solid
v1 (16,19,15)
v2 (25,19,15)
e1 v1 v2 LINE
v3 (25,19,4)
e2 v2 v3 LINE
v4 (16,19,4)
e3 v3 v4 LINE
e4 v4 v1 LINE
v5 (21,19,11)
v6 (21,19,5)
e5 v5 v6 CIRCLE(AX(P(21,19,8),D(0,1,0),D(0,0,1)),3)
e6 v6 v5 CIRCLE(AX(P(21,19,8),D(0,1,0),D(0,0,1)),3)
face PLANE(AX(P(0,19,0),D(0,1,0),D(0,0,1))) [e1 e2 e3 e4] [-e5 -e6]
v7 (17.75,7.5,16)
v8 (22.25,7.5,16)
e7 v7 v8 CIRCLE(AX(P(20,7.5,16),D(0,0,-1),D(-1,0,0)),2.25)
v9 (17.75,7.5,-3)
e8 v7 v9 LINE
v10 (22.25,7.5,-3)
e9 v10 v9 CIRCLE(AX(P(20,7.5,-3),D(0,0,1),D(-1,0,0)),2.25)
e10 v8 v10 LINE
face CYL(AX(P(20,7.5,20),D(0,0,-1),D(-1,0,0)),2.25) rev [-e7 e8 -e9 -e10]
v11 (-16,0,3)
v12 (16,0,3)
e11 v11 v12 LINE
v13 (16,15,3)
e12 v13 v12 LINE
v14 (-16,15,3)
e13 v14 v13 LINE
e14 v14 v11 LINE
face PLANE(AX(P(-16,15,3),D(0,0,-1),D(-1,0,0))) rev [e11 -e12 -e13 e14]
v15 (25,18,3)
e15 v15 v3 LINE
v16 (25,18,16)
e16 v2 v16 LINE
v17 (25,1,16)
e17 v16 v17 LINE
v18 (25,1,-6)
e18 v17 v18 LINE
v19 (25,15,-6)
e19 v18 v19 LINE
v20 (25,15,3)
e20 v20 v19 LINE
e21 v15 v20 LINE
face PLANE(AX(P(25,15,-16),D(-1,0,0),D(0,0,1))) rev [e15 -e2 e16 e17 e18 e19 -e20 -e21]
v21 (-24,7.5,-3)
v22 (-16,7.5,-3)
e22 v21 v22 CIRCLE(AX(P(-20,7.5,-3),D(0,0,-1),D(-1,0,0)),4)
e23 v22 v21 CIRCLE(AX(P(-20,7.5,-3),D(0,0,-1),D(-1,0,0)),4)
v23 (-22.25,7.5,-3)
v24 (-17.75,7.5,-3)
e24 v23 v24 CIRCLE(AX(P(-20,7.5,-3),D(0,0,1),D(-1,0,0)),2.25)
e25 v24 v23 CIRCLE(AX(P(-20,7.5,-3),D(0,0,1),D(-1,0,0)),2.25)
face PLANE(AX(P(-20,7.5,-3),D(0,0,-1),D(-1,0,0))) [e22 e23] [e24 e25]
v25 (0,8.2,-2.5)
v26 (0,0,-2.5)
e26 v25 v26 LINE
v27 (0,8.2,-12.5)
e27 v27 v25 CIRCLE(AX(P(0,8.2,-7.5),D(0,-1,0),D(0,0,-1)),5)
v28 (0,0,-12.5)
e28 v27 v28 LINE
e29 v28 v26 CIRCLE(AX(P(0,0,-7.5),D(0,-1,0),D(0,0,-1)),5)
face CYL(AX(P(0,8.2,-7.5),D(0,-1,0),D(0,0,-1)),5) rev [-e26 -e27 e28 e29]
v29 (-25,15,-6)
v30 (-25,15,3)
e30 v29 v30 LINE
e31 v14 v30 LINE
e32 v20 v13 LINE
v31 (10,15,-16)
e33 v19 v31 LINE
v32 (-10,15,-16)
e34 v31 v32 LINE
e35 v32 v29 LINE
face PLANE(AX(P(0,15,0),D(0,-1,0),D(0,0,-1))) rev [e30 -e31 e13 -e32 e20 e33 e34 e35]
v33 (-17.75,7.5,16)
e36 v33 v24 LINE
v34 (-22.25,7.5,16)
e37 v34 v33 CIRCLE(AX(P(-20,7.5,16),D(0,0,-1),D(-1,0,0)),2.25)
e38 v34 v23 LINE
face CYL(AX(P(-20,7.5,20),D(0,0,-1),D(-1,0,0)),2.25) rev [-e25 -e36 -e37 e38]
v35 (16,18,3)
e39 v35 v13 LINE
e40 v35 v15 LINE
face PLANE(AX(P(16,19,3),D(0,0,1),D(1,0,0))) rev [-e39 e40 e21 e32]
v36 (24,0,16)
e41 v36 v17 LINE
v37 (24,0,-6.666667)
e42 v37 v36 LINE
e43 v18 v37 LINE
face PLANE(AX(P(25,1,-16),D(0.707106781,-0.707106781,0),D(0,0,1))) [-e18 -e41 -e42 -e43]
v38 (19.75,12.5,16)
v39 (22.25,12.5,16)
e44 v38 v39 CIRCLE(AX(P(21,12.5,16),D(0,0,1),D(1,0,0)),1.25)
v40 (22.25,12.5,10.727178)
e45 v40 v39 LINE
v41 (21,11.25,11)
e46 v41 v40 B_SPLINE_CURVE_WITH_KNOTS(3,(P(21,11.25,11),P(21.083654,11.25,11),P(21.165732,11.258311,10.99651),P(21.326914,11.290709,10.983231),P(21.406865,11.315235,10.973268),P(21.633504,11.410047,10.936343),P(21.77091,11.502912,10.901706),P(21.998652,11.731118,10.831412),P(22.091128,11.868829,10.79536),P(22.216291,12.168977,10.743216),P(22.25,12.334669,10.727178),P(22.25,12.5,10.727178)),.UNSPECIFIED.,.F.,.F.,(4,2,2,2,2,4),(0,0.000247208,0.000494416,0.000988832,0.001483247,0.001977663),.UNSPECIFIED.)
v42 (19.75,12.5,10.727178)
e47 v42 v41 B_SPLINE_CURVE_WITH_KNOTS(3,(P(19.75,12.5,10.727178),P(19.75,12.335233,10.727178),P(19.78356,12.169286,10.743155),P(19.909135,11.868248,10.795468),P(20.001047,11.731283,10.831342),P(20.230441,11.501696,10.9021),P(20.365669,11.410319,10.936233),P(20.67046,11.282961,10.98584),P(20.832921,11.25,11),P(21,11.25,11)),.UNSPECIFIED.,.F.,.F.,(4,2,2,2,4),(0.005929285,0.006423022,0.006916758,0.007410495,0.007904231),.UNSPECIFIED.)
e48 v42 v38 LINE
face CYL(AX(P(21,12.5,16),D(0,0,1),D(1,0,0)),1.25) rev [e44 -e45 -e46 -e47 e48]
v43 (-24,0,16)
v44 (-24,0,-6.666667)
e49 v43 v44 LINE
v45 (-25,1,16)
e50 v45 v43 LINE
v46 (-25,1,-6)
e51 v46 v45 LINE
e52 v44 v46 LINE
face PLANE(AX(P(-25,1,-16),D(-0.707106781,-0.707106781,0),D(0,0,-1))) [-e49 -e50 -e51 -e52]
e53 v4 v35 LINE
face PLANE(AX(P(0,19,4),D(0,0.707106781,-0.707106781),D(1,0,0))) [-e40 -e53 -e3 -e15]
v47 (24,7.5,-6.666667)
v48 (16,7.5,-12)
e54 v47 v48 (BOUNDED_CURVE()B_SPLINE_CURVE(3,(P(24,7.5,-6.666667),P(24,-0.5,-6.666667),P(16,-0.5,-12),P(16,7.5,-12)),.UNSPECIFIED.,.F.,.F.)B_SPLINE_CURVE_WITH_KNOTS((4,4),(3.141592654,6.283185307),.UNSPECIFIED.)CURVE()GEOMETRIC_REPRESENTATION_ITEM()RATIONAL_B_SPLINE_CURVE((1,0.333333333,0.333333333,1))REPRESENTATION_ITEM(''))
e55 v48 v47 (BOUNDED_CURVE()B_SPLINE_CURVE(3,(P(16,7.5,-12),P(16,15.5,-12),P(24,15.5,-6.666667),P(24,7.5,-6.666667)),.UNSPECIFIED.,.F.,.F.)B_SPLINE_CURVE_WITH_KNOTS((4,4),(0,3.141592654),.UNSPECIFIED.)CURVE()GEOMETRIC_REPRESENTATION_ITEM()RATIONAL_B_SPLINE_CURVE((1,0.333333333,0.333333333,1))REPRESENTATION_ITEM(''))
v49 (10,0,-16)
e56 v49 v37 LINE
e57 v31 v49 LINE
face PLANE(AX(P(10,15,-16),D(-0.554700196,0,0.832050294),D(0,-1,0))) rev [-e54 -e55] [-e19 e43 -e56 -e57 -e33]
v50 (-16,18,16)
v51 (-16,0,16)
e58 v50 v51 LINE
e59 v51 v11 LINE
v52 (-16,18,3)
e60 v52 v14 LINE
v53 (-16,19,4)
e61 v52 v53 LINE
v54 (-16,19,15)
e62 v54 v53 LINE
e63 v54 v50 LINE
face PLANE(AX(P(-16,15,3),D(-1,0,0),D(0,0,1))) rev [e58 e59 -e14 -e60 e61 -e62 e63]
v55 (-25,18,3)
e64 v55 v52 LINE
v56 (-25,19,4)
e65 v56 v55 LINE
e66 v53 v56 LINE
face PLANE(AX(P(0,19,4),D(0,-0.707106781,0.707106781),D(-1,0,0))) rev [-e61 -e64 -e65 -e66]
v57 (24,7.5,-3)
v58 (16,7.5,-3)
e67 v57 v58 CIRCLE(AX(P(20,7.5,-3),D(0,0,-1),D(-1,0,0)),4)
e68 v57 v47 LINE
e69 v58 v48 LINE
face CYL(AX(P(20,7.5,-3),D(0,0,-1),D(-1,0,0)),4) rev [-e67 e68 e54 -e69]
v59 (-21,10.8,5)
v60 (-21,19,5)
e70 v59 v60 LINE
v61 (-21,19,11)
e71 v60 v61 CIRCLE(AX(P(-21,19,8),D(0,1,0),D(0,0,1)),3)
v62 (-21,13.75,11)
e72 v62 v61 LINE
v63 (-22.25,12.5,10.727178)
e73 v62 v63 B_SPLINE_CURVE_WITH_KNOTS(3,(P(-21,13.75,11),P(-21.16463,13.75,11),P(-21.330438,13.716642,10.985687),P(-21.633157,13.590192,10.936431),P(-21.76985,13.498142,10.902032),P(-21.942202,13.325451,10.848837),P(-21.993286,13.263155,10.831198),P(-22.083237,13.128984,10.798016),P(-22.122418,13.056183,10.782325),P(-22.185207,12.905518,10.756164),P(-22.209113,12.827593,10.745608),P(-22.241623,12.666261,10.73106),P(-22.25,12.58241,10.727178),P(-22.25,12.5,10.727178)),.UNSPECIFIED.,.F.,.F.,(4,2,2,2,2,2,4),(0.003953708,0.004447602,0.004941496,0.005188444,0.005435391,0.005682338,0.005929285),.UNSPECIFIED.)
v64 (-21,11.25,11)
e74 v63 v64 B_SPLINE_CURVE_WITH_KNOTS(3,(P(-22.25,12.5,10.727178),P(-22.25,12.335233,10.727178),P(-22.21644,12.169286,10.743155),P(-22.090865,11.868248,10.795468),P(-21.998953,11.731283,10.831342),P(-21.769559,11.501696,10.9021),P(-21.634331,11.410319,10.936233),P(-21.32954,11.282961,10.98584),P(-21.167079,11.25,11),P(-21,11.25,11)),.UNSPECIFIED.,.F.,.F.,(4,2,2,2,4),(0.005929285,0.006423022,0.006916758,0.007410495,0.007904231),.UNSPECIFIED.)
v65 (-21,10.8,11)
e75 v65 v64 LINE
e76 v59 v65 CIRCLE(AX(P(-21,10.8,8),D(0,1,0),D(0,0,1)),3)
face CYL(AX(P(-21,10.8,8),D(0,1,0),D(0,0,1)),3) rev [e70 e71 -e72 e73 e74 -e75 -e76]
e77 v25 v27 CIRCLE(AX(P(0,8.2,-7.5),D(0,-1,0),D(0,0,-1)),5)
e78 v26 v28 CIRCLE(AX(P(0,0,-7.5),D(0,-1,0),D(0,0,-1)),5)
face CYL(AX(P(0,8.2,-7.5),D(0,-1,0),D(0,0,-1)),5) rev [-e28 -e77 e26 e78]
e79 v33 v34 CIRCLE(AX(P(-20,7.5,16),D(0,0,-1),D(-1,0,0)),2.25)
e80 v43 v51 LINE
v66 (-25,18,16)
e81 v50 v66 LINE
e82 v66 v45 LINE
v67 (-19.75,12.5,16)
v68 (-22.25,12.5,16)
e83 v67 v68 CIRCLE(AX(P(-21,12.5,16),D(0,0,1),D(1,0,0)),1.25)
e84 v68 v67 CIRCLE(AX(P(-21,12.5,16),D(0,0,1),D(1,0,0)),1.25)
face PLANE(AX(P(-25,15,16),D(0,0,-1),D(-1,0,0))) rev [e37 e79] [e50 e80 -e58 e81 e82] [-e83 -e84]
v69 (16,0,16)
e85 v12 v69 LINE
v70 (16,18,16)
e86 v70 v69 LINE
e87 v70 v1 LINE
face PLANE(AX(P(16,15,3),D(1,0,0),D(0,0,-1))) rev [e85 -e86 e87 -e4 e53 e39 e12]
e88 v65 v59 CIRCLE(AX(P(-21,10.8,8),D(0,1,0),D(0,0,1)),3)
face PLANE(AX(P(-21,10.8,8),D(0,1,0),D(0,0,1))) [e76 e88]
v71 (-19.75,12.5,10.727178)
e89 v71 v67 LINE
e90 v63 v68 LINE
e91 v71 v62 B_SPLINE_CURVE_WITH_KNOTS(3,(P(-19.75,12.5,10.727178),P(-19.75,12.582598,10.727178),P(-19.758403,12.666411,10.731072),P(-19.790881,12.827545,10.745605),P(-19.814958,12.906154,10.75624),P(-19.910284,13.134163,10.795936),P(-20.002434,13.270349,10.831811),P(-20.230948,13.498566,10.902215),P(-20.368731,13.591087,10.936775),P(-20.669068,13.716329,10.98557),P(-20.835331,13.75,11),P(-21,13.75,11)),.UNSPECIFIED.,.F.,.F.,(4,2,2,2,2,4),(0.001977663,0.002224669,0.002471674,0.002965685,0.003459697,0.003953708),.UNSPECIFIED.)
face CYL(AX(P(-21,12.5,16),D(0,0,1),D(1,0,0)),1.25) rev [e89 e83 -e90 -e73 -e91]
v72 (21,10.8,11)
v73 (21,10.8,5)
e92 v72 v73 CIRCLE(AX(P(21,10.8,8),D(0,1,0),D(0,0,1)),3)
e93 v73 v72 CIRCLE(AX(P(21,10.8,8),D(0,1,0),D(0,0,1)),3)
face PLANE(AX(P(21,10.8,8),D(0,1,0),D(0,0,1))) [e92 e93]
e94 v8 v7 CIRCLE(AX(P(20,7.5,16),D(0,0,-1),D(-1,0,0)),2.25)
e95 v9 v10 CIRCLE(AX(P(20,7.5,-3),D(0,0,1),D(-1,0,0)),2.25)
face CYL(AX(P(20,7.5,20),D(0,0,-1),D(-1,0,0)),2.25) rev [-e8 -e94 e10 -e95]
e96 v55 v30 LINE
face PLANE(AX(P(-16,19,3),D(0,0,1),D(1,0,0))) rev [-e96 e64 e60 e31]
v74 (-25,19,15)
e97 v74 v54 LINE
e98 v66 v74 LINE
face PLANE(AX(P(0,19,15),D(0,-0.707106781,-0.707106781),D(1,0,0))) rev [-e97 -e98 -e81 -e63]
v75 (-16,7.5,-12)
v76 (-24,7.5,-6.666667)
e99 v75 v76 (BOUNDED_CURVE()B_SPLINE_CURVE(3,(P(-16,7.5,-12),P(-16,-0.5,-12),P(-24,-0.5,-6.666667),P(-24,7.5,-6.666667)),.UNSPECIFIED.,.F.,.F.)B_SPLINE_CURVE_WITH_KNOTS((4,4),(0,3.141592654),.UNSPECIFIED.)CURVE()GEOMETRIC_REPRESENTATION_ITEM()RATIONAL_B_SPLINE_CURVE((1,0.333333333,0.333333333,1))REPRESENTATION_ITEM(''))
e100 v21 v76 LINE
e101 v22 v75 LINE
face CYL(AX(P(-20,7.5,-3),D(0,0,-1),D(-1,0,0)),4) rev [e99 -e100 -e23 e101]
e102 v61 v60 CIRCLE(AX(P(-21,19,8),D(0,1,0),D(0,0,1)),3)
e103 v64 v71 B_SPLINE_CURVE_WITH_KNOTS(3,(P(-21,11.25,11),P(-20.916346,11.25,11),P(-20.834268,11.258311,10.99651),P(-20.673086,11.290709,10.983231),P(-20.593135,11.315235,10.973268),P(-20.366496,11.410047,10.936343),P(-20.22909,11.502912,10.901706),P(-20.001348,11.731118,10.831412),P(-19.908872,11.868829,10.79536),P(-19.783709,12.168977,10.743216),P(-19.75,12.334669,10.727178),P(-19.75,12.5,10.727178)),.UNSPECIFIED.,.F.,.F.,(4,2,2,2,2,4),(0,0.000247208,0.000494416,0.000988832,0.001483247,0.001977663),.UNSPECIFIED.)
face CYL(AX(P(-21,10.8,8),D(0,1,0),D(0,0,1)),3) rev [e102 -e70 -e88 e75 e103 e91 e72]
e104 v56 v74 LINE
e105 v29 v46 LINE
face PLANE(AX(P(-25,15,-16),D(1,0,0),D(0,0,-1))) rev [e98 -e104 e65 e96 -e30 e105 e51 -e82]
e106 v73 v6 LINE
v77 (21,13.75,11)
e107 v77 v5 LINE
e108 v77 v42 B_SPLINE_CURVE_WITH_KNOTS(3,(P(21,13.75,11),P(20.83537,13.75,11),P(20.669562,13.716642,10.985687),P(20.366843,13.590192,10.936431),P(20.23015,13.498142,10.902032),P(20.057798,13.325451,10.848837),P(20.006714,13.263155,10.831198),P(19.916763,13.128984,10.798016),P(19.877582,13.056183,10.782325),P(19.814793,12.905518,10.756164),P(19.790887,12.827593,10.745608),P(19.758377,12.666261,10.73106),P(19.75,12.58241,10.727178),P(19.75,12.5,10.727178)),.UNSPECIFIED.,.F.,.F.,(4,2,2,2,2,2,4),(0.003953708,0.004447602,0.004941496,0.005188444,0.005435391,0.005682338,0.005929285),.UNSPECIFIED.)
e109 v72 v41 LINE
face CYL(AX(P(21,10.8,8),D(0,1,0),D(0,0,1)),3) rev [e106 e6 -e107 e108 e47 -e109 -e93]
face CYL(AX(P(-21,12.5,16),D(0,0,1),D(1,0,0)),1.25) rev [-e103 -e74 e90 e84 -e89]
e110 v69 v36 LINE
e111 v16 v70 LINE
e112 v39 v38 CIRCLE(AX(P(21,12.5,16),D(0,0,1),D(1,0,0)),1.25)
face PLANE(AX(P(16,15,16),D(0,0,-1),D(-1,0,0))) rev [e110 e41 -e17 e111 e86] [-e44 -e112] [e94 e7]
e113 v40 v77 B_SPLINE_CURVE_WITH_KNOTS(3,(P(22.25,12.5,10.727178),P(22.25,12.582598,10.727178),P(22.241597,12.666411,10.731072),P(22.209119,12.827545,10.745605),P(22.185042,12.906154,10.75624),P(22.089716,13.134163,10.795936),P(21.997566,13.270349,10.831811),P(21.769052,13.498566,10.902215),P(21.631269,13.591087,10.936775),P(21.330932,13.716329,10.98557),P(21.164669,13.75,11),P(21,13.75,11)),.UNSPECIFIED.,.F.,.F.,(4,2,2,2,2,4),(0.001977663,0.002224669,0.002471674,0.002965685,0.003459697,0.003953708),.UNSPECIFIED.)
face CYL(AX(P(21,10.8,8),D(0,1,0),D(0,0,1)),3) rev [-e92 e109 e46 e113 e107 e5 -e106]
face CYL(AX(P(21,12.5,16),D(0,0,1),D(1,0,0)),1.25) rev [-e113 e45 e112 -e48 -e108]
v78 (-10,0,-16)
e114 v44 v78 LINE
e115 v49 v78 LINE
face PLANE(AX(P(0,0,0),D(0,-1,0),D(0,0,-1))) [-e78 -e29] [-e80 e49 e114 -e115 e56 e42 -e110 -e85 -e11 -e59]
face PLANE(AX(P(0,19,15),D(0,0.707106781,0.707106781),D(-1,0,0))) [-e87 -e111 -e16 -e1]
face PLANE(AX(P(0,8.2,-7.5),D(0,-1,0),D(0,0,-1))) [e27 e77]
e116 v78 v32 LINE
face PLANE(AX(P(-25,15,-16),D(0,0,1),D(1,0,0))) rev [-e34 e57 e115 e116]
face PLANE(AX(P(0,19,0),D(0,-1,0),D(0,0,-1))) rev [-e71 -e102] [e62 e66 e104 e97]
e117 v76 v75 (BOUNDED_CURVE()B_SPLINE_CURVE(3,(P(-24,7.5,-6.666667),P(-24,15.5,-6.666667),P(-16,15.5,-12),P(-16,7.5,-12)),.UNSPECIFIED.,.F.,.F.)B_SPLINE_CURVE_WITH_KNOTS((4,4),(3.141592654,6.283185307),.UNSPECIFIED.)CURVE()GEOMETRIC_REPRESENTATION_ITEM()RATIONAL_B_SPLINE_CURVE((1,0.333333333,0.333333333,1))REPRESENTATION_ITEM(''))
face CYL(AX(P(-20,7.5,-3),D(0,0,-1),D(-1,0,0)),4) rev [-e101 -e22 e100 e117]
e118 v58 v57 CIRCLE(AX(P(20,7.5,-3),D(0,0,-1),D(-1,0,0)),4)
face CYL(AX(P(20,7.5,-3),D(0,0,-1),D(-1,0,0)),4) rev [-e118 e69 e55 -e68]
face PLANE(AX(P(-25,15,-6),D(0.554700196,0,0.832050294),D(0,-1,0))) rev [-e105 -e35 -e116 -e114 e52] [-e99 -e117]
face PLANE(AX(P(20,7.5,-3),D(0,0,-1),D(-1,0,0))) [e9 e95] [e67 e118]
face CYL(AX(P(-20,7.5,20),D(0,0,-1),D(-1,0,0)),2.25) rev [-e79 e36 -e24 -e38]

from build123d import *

# Parameters (mm, degrees)
BOSS_EXTRUDE1_DEPTH   = 15
CHAMFER1_SIZE         = 10
CHAMFER1_SIZE2        = 15
CHAMFER2_SIZE         = 15
CHAMFER2_SIZE2        = 10
SKETCH2_R             = 2.25
CUT_EXTRUDE1_DEPTH    = 36
SKETCH3_R             = 4
CUT_EXTRUDE2_DEPTH    = 13
SKETCH12_R            = 3
CUT_EXTRUDE7_DEPTH    = 4.2
M3_TAPPED_HOLE1_D     = 2.5
M3_TAPPED_HOLE1_DEPTH = 7.5
M3_TAPPED_HOLE1_TIP   = 0.751075774
M3_TAPPED_HOLE2_D     = 2.5
M3_TAPPED_HOLE2_DEPTH = 7.5
M3_TAPPED_HOLE2_TIP   = 0.751075774
BOSS_EXTRUDE3_START   = 4
SKETCH17_W            = 9
SKETCH17_H            = 13
SKETCH17_R            = 3
BOSS_EXTRUDE3_DEPTH   = 4
SKETCH18_R            = 5
CUT_EXTRUDE8_DEPTH    = 8.2
CHAMFER3_SIZE         = 1


with BuildPart() as part:
    # Sketch1 → Boss-Extrude1 (new body)
    with BuildSketch(Plane(origin=(0, 0, 0), x_dir=(1, 0, 0), z_dir=(0, 1, 0))):
        Polygon((-25, 16), (25, 16), (25, -16), (16, -16), (16, -3), (-16, -3), (-16, -16), (-25, -16), align=None)
    extrude(amount=BOSS_EXTRUDE1_DEPTH)

    # Chamfer1
    chamfer1_edges = [part.edges().sort_by_distance(p)[0] for p in [
        (25, 7.5, -16),
    ]]
    chamfer1_side = [part.faces().sort_by_distance(p)[0] for p in [
        (25, 7.5, 0),
    ]]
    chamfer(chamfer1_edges, length=CHAMFER1_SIZE, length2=CHAMFER1_SIZE2, reference=chamfer1_side[0])

    # Chamfer2
    chamfer2_edges = [part.edges().sort_by_distance(p)[0] for p in [
        (-25, 7.5, -16),
    ]]
    chamfer2_side = [part.faces().sort_by_distance(p)[0] for p in [
        (-7.5, 7.5, -16),
    ]]
    chamfer(chamfer2_edges, length=CHAMFER2_SIZE, length2=CHAMFER2_SIZE2, reference=chamfer2_side[0])

    # Sketch2 → Cut-Extrude1 (cut)
    with BuildSketch(Plane(origin=(0, 0, -16), x_dir=(-1, 0, 0), z_dir=(0, 0, -1))):
        with Locations((-20, 7.5)):
            Circle(SKETCH2_R)
        with Locations((20, 7.5)):
            Circle(SKETCH2_R)
    extrude(amount=-CUT_EXTRUDE1_DEPTH, mode=Mode.SUBTRACT)

    # Sketch3 → Cut-Extrude2 (cut)
    with BuildSketch(Plane(origin=(0, 0, -16), x_dir=(-1, 0, 0), z_dir=(0, 0, -1))):
        with Locations((-20, 7.5)):
            Circle(SKETCH3_R)
        with Locations((20, 7.5)):
            Circle(SKETCH3_R)
    extrude(amount=-CUT_EXTRUDE2_DEPTH, mode=Mode.SUBTRACT)

    # Sketch12 → Cut-Extrude7 (cut)
    with BuildSketch(Plane(origin=(0, 15, 0), x_dir=(1, 0, 0), z_dir=(0, 1, 0))):
        with Locations(Location((-21, -8, 0), (0, 0, 270))):
            Circle(SKETCH12_R)
        with Locations(Location((21, -8, 0), (0, 0, 270))):
            Circle(SKETCH12_R)
    extrude(amount=-CUT_EXTRUDE7_DEPTH, mode=Mode.SUBTRACT)

    # M3 Tapped Hole1
    with Locations(Plane(origin=(-21, 12.5, 16), x_dir=(1, 0, 0), z_dir=(0, 0, 1))):
        with Locations((0, 0)):
            Hole(M3_TAPPED_HOLE1_D / 2, depth=M3_TAPPED_HOLE1_DEPTH)
            with Locations((0, 0, -(M3_TAPPED_HOLE1_DEPTH + M3_TAPPED_HOLE1_TIP / 2))):  # 118° drill point
                Cone(0, M3_TAPPED_HOLE1_D / 2, M3_TAPPED_HOLE1_TIP, mode=Mode.SUBTRACT)

    # M3 Tapped Hole2
    with Locations(Plane(origin=(21, 12.5, 16), x_dir=(1, 0, 0), z_dir=(0, 0, 1))):
        with Locations((0, 0)):
            Hole(M3_TAPPED_HOLE2_D / 2, depth=M3_TAPPED_HOLE2_DEPTH)
            with Locations((0, 0, -(M3_TAPPED_HOLE2_DEPTH + M3_TAPPED_HOLE2_TIP / 2))):  # 118° drill point
                Cone(0, M3_TAPPED_HOLE2_D / 2, M3_TAPPED_HOLE2_TIP, mode=Mode.SUBTRACT)

    # Sketch17 → Boss-Extrude3 (add)
    # profile 1 of 2: a face of its own
    with BuildSketch(Plane(origin=(0, 15, 0), x_dir=(1, 0, 0), z_dir=(0, 1, 0)).offset(BOSS_EXTRUDE3_START)):
        with Locations((-20.5, -9.5)):
            Rectangle(SKETCH17_W, SKETCH17_H)
        with Locations(Location((-21, -8, 0), (0, 0, 270))):
            Circle(SKETCH17_R, mode=Mode.SUBTRACT)
    # profile 2 of 2: a face of its own
    with BuildSketch(Plane(origin=(0, 15, 0), x_dir=(1, 0, 0), z_dir=(0, 1, 0)).offset(BOSS_EXTRUDE3_START)):
        with Locations((20.5, -9.5)):
            Rectangle(SKETCH17_W, SKETCH17_H)
        with Locations(Location((21, -8, 0), (0, 0, 270))):
            Circle(SKETCH17_R, mode=Mode.SUBTRACT)
    extrude(amount=-BOSS_EXTRUDE3_DEPTH)

    # Sketch18 → Cut-Extrude8 (cut)
    with BuildSketch(Plane.XZ):
        with Locations(Location((0, -7.5, 0), (0, 0, 270))):
            Circle(SKETCH18_R)
    extrude(amount=-CUT_EXTRUDE8_DEPTH, mode=Mode.SUBTRACT)

    # Chamfer3
    chamfer3_edges = [part.edges().sort_by_distance(p)[0] for p in [
        (-20.5, 19, 3),
        (20.5, 19, 3),
        (-20.5, 19, 16),
        (20.5, 19, 16),
        (-25, 0, 5),
        (25, 0, 5),
    ]]
    chamfer(chamfer3_edges, length=CHAMFER3_SIZE)


solid = part.part
